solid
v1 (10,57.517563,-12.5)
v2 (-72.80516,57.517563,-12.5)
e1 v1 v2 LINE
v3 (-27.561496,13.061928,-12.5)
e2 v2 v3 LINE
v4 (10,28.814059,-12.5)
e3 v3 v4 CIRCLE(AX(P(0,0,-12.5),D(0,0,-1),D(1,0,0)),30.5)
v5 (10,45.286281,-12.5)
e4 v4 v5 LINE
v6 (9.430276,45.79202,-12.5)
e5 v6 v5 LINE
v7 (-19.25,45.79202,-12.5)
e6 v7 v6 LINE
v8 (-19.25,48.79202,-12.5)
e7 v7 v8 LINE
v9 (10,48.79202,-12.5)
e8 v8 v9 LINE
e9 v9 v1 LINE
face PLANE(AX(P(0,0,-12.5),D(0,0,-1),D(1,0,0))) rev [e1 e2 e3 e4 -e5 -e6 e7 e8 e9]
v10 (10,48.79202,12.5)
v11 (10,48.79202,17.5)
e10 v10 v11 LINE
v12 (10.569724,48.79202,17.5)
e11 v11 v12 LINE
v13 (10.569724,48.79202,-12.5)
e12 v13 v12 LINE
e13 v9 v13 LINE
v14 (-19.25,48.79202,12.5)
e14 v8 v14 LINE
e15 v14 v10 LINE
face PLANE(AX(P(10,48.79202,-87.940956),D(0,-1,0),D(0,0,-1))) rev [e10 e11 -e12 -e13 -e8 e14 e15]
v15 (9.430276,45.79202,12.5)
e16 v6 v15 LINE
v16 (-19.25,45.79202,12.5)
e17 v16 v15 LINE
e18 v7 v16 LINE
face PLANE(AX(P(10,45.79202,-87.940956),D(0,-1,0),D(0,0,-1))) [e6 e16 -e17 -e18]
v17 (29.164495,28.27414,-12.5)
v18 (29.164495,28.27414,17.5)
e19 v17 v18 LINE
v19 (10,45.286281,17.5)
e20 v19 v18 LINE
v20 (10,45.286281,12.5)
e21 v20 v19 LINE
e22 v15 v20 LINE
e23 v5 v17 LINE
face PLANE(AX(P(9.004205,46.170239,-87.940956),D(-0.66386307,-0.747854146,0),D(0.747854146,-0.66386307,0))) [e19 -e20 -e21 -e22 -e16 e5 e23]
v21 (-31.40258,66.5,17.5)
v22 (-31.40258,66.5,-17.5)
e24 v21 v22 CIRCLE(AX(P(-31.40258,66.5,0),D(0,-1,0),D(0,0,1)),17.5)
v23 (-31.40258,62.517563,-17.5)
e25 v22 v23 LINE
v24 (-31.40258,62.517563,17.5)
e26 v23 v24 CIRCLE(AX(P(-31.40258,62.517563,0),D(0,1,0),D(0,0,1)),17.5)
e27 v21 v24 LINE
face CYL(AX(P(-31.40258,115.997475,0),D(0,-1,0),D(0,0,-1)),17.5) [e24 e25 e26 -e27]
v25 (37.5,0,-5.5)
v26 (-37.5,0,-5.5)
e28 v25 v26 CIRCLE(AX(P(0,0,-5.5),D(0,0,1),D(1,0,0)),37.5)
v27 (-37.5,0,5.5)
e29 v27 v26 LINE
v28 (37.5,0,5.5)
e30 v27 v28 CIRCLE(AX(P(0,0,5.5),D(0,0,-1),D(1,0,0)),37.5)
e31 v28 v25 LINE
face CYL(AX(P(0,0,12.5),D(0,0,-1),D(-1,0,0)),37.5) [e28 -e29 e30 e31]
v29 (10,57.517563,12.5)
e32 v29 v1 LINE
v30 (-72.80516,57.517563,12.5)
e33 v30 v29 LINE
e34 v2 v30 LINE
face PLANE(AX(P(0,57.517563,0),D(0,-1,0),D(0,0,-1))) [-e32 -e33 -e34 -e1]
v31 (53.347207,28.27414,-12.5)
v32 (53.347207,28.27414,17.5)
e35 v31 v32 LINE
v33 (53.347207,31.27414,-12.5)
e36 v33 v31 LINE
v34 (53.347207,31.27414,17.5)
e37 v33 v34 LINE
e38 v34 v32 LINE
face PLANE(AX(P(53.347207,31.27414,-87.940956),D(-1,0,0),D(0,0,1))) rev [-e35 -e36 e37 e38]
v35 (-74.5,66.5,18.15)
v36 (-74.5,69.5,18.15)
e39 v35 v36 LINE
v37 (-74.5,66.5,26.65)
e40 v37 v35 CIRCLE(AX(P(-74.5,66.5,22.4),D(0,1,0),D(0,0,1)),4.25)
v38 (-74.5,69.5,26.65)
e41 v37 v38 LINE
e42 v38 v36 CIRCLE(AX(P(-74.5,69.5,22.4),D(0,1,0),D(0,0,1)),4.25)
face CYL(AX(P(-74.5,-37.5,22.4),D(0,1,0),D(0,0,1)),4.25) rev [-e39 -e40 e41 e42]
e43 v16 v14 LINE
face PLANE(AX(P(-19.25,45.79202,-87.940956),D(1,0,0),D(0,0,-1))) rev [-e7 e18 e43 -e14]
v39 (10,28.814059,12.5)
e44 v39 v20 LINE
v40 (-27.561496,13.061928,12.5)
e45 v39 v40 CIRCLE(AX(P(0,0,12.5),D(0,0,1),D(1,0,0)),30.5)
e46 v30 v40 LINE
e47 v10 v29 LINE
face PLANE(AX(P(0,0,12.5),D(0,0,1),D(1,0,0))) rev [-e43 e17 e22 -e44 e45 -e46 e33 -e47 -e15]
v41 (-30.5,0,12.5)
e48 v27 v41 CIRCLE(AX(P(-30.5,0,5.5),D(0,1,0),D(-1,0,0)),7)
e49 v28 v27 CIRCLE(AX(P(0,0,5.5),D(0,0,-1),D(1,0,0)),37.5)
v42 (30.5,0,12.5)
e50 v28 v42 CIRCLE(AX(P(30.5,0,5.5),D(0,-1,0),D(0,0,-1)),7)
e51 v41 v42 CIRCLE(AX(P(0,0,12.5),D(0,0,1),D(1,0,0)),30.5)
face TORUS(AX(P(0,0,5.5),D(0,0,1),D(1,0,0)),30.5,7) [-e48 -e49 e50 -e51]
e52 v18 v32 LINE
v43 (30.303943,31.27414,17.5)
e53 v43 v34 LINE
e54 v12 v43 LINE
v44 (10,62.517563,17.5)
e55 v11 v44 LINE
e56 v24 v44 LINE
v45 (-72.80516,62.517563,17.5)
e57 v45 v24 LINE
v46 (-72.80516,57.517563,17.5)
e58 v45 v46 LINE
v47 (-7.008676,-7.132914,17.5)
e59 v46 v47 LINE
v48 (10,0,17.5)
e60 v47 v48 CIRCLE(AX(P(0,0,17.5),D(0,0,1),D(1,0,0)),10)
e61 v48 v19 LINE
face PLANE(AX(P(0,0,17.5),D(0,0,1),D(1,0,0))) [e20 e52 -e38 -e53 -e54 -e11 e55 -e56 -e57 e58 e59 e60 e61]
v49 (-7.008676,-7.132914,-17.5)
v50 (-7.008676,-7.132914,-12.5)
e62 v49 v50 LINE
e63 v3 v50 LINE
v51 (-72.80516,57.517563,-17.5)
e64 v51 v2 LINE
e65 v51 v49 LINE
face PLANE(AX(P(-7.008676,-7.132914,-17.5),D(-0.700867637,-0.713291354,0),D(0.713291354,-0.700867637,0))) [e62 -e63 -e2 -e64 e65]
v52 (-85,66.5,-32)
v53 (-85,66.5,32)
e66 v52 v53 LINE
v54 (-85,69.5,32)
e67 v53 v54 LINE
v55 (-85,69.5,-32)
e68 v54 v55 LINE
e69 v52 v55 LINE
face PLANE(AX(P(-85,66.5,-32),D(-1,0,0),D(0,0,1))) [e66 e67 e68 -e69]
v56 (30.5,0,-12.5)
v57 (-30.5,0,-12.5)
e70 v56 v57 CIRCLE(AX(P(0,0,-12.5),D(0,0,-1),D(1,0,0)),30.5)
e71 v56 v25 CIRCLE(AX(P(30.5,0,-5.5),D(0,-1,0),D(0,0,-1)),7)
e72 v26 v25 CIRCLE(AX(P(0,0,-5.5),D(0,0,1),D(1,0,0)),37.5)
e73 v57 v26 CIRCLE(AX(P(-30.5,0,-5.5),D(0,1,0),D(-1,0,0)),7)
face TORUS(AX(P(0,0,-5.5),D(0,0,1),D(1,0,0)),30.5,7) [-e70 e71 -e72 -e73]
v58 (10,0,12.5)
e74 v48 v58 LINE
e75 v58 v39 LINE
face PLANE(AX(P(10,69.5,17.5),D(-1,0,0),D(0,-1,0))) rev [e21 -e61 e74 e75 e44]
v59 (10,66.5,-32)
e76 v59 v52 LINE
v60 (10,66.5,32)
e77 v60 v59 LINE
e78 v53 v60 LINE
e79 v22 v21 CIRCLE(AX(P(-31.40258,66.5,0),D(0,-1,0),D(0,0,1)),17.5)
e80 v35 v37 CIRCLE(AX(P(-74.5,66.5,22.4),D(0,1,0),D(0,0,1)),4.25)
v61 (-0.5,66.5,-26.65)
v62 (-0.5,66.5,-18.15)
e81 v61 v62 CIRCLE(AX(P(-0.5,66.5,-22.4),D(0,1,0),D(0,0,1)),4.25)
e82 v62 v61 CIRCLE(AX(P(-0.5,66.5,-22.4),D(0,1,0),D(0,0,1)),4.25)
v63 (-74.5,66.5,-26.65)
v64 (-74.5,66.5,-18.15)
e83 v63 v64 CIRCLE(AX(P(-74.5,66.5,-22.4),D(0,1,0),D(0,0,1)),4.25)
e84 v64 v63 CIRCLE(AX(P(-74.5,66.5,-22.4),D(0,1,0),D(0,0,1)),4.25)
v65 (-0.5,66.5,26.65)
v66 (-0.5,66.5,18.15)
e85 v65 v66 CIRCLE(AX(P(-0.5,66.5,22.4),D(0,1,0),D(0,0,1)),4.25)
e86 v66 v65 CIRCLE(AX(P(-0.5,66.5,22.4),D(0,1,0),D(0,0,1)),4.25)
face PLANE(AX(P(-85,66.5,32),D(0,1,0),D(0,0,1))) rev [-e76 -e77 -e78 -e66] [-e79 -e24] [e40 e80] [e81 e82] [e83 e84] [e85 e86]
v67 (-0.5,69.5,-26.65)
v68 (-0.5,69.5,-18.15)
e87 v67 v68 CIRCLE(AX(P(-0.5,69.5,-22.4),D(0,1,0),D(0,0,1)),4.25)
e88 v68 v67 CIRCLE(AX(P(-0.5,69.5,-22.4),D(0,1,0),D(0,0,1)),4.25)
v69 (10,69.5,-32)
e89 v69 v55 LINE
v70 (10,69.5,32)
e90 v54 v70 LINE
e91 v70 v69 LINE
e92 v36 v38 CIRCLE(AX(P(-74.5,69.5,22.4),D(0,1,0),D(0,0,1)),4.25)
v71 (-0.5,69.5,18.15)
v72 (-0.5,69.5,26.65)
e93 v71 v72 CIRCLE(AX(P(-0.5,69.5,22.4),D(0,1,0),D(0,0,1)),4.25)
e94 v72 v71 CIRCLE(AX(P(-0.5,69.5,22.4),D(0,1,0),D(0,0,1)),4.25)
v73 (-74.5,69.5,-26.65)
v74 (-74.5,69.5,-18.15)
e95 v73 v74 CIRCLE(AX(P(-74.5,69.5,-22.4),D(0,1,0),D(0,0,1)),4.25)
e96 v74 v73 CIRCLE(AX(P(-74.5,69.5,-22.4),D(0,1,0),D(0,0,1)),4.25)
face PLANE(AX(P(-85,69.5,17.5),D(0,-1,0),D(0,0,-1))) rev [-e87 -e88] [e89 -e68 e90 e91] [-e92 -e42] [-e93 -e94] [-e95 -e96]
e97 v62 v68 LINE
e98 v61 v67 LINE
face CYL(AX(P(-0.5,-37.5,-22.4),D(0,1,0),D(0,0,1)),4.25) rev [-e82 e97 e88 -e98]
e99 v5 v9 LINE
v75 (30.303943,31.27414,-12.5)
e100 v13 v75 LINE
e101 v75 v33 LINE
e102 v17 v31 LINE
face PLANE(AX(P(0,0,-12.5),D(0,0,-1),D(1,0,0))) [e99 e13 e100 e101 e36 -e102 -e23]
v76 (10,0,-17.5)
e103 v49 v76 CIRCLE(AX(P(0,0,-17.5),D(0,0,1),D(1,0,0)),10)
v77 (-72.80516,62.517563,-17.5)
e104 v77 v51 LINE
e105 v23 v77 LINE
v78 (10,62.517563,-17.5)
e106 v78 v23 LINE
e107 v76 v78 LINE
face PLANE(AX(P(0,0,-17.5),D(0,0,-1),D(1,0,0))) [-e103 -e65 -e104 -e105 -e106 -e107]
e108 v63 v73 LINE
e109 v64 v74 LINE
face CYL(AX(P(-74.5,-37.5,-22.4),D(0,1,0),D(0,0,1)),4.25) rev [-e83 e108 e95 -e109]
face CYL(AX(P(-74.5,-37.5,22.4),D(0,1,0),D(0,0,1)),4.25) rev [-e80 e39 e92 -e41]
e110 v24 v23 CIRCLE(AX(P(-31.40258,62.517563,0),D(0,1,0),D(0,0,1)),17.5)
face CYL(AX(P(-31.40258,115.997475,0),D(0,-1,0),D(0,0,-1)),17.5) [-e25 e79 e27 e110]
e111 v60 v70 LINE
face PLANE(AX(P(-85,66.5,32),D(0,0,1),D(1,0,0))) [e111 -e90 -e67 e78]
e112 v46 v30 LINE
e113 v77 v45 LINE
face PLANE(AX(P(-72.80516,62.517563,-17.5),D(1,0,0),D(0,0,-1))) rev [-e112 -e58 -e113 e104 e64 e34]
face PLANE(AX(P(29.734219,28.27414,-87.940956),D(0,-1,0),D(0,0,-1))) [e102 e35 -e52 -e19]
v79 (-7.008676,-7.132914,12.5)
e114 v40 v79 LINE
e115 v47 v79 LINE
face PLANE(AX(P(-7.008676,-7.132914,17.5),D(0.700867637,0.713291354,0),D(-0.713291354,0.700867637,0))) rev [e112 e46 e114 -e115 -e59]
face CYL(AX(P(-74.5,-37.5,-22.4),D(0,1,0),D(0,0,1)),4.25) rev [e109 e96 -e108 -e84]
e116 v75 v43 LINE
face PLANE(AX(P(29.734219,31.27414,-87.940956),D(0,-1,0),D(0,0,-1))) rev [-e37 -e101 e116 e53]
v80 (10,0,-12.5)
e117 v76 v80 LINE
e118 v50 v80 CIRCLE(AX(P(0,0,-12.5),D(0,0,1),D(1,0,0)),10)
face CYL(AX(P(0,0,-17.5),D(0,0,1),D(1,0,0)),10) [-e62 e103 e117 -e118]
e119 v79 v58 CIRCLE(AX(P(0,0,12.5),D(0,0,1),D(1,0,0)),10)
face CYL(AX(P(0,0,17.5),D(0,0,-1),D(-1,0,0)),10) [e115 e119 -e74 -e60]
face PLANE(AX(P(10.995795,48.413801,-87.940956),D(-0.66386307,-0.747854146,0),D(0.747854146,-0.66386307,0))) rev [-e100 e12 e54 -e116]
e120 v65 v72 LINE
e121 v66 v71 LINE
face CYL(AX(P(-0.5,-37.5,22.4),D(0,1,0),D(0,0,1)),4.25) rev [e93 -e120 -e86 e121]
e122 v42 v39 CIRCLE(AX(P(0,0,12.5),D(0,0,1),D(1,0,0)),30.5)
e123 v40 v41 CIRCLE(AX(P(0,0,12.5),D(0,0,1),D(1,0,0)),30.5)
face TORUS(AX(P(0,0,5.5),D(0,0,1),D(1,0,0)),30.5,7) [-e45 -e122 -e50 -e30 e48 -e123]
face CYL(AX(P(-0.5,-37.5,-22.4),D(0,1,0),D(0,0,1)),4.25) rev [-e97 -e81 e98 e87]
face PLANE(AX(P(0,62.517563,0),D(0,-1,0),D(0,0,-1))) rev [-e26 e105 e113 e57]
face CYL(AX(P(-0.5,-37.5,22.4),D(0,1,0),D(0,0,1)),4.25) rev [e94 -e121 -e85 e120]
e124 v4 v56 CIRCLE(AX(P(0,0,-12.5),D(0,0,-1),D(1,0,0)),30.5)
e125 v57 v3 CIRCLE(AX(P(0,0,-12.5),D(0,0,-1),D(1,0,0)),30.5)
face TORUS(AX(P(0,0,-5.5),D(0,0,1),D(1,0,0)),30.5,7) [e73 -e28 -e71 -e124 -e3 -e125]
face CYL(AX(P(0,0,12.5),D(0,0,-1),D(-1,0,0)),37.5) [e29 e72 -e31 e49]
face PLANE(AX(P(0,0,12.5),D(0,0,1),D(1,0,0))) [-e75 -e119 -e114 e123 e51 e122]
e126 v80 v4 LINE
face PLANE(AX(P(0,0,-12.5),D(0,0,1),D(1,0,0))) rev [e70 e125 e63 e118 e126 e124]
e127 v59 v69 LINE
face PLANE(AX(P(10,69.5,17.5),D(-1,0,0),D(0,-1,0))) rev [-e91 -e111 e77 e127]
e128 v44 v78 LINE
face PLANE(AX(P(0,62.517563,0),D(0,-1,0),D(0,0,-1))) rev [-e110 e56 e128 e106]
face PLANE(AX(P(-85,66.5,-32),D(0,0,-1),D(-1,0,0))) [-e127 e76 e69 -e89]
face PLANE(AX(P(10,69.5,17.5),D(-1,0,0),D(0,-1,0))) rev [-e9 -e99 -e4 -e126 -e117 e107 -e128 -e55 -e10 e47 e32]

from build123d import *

# Parameters (mm, degrees)
SKETCH_1_R          = 37.5
EXTRUDE_1_DEPTH     = 12.5
FILLET_1_R          = 7
SKETCH_2_R          = 5.411787985
EXTRUDE_2_DEPTH     = 15
EXTRUDE_3_DEPTH     = 5
SKETCH_4_W          = 95
SKETCH_4_H          = 64
EXTRUDE_4_DEPTH     = 3
SKETCH_6_R          = 4.25
CUT_EXTRUDE_1_DEPTH = 141.349563667
SKETCH_9_W          = 92.539395388
SKETCH_9_H          = 8.982437317
CUT_EXTRUDE_2_DEPTH = 121.43878113
SKETCH_10_W         = 82.805159643
SKETCH_10_H         = 35
EXTRUDE_5_DEPTH     = 5
SKETCH_11_R         = 17.5
EXTRUDE_6_DEPTH     = 3.982437317
EXTRUDE_1_2_DEPTH   = 30


with BuildPart() as part:
    # 草图1 → Extrude 1 (new, symmetric)
    with BuildSketch(Plane.XY):
        Circle(SKETCH_1_R)
    extrude(amount=EXTRUDE_1_DEPTH, both=True)

    # 圆角1
    fillet_1_edges = [part.edges().sort_by_distance(p)[0] for p in [
        (-37.5, 0, -12.5),
        (-37.5, 0, 12.5),
    ]]
    fillet(fillet_1_edges, radius=FILLET_1_R)

    # 草图2 → 凸台-拉伸2 (add, symmetric)
    with BuildSketch(Plane.XY):
        Circle(SKETCH_2_R)
    extrude(amount=EXTRUDE_2_DEPTH, both=True)

    # 草图3 → 凸台-拉伸3 (add)
    with BuildSketch(Plane.XY.offset(12.5)):
        with BuildLine():
            Line((-7.008676366, -7.132913542), (-85, 69.5))
            Line((-85, 69.5), (10, 69.5))
            Line((10, 69.5), (10, 0))
            ThreePointArc((10, 0), (3.867378721, -9.221896867), (-7.008676366, -7.132913542))
        make_face()
    extrude_3 = extrude(amount=EXTRUDE_3_DEPTH)

    # 镜向1: 凸台-拉伸3 across plane
    add(extrude_3.mirror(Plane.XY))

    # 草图4 → 凸台-拉伸4 (add)
    with BuildSketch(Plane(origin=(0, 69.5, 0), x_dir=(1, 0, 0), z_dir=(0, 1, 0))):
        with Locations((-37.5, 0)):
            Rectangle(SKETCH_4_W, SKETCH_4_H)
    extrude(amount=-EXTRUDE_4_DEPTH)

    # 草图6 → 切除-拉伸1 (cut, through all)
    with BuildSketch(Plane(origin=(0, 69.5, 0), x_dir=(1, 0, 0), z_dir=(0, 1, 0))):
        with Locations(Location((-0.5, -22.4, 0), (0, 0, 270))):
            Circle(SKETCH_6_R)
        with Locations(Location((-0.5, 22.4, 0), (0, 0, 270))):
            Circle(SKETCH_6_R)
        with Locations(Location((-74.5, 22.4, 0), (0, 0, 270))):
            Circle(SKETCH_6_R)
        with Locations(Location((-74.5, -22.4, 0), (0, 0, 270))):
            Circle(SKETCH_6_R)
    extrude(amount=-CUT_EXTRUDE_1_DEPTH, mode=Mode.SUBTRACT)

    # 草图9 → 切除-拉伸2 (cut, through all)
    with BuildSketch(Plane.XY.offset(17.5)):
        with Locations((-36.269697694, 62.008781341)):
            Rectangle(SKETCH_9_W, SKETCH_9_H)
    extrude(amount=-CUT_EXTRUDE_2_DEPTH, mode=Mode.SUBTRACT)


with BuildPart() as cut_extrude_2_piece_1:
    # of the separate pieces the step leaves, piece 1, a body of its own (cut_extrude_2_pieces)
    add(part.part.solids().sort_by_distance((37.5, 0, -5.5))[0])

    # 草图10 → 凸台-拉伸5 (add)
    with BuildSketch(Plane(origin=(0, 57.517562683, 0), x_dir=(1, 0, 0), z_dir=(0, 1, 0))):
        with Locations((-31.402579822, 0)):
            Rectangle(SKETCH_10_W, SKETCH_10_H)
    extrude(amount=EXTRUDE_5_DEPTH)



with BuildPart() as cut_extrude_2_piece_2:
    # of the separate pieces the step leaves, piece 2, a body of its own (cut_extrude_2_pieces)
    add(part.part.solids().sort_by_distance((10, 66.5, 32))[0])


with BuildPart() as cut_extrude_2_piece_1_1:
    add(cut_extrude_2_piece_1.part)

    add(cut_extrude_2_piece_2.part)  # 凸台-拉伸6 merges 切除-拉伸2 piece 2
    # 草图11 → 凸台-拉伸6 (add)
    with BuildSketch(Plane(origin=(0, 62.517562683, 0), x_dir=(1, 0, 0), z_dir=(0, 1, 0))):
        with Locations(Location((-31.402579821, 0, 0), (0, 0, 270))):
            Circle(SKETCH_11_R)
    extrude(amount=EXTRUDE_6_DEPTH)

    # 草图8 → Extrude 1 2 (add)
    with BuildSketch(Plane.XY.offset(17.5)):
        Polygon((-19.25, 45.79201997), (9.430275915, 45.79201997), (29.164495175, 28.274139716), (53.347206554, 28.274139716), (53.347206554, 31.274139716), (30.303943346, 31.274139716), (10.569724085, 48.79201997), (-19.25, 48.79201997), align=None)
    extrude(amount=-EXTRUDE_1_2_DEPTH)


solid = cut_extrude_2_piece_1_1.part
